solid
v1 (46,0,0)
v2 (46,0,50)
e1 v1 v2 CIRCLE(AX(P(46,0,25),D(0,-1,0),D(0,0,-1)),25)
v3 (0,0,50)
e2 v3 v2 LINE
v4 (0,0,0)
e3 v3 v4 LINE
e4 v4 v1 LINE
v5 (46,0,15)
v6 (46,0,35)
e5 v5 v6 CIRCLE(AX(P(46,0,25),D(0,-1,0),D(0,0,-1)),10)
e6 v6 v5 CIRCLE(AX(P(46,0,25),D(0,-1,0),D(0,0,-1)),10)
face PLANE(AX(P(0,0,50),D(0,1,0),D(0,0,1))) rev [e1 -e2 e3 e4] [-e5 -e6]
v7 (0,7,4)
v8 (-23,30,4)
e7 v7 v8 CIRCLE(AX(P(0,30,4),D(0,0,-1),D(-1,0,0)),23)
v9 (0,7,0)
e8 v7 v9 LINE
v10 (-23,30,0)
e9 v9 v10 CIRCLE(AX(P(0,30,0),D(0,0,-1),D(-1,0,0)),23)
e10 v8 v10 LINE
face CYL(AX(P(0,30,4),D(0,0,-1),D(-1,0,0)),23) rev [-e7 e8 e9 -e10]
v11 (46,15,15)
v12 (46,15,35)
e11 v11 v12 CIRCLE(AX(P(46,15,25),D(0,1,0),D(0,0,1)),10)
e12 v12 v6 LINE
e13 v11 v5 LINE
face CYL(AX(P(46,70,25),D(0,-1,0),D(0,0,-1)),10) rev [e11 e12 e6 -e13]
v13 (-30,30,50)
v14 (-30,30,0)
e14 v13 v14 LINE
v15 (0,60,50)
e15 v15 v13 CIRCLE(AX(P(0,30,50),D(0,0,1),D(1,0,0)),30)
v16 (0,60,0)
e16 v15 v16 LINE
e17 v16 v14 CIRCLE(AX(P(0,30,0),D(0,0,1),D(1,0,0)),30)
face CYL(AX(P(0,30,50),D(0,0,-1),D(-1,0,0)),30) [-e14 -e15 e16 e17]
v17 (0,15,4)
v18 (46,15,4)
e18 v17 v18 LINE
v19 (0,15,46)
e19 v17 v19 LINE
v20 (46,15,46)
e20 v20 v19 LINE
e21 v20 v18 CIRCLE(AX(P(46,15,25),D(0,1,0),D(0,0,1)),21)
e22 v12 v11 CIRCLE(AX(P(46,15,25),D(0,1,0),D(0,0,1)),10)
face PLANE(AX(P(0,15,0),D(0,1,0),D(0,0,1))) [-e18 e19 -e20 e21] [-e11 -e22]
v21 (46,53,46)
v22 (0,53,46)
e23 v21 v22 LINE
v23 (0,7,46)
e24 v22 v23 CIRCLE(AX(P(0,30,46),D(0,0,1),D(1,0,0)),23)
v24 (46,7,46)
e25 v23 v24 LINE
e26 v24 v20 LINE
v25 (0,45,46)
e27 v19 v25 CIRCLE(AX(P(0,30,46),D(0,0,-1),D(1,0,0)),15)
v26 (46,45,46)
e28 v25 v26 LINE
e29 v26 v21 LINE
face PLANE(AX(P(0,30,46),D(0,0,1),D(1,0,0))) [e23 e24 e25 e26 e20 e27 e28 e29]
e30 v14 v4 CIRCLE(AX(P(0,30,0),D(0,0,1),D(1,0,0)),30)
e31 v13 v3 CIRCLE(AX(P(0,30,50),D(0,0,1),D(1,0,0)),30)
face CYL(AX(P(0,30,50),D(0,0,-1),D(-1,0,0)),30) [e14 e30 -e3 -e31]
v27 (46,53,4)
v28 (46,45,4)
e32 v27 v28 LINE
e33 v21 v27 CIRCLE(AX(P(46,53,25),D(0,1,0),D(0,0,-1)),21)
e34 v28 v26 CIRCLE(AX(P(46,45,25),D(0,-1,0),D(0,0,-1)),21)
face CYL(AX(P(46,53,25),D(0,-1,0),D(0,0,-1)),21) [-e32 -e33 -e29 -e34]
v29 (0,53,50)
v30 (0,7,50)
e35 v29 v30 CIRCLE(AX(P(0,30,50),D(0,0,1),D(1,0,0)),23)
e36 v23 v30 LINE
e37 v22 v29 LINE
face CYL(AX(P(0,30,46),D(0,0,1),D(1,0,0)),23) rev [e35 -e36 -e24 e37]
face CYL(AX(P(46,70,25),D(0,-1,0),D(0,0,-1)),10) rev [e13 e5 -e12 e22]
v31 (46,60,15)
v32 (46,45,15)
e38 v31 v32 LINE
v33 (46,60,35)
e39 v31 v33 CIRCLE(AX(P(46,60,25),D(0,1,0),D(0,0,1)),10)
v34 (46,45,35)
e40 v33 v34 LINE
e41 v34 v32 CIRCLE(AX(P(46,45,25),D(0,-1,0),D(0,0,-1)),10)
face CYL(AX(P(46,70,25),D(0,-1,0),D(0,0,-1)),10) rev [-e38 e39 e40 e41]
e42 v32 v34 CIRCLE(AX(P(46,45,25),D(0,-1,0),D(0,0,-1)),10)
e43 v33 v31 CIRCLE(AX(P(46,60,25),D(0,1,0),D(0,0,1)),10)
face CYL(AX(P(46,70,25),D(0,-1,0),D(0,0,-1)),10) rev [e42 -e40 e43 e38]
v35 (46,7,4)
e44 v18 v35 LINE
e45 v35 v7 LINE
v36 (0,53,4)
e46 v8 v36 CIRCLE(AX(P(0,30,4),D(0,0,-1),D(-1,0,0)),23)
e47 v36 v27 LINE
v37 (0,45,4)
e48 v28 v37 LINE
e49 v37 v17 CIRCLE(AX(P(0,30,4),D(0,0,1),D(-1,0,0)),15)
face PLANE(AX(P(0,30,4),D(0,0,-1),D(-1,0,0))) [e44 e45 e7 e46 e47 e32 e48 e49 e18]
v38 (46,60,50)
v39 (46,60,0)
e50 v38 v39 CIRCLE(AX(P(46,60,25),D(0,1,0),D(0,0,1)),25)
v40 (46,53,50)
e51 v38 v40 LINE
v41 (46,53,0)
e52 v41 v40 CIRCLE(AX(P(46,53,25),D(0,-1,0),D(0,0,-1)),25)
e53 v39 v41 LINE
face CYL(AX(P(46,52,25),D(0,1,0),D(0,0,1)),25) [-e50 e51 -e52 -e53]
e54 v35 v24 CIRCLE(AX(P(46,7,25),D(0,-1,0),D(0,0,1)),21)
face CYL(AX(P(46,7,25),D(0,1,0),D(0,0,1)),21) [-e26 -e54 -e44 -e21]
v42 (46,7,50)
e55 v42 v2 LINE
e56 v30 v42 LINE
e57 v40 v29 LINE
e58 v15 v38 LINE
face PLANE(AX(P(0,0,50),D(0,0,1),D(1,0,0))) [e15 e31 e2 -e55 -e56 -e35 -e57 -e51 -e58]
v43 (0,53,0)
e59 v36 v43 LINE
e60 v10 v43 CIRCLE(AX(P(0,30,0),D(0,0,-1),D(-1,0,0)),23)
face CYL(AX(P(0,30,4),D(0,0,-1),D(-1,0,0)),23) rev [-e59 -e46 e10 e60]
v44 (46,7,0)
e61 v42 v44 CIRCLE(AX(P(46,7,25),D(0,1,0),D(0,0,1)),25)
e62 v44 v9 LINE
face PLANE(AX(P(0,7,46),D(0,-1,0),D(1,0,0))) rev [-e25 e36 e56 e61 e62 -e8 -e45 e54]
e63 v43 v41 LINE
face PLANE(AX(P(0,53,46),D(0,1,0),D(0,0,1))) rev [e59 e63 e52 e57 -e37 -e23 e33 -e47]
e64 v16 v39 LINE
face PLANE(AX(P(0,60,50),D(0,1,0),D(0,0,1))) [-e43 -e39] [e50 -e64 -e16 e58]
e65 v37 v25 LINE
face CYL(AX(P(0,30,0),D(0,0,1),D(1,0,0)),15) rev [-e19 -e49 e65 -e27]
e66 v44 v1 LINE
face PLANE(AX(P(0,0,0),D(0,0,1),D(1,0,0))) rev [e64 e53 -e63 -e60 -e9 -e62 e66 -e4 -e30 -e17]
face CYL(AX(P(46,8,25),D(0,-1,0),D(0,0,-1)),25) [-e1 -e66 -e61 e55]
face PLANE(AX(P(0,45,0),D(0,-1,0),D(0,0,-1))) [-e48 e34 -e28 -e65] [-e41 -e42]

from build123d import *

# Parameters (mm, degrees)
U_FORK_BASE_DEPTH   = 50
U_START             = -50
U_WRAP_LAYER_DEPTH  = 50
WRAP_START          = -4
WRAP_RECESS_1_DEPTH = 4
WRAP_RECESS_2_DEPTH = 4
ARM_PAD_1_DEPTH     = 8
ARM_PAD_2_DEPTH     = 8
ARM_START           = -8
ARM_PAD_3_DEPTH     = 8
ARM_PAD_4_DEPTH     = 8
ARM_PAD_5_DEPTH     = 8
PIN_HOLE_SKETCH_R   = 10
PIN_HOLE_DEPTH      = 70
FACE_RELIEF_1_DEPTH = 1
FACE_START          = -1
FACE_RELIEF_2_DEPTH = 1


with BuildPart() as part:
    # U Fork Profile Sketch → U Fork Base (new body)
    with BuildSketch(Plane.XY):
        with BuildLine():
            ThreePointArc((0, 53), (-23, 30), (0, 7))
            Line((0, 7), (46, 7))
            Line((46, 7), (46, 0))
            Line((46, 0), (0, 0))
            ThreePointArc((0, 0), (-30, 30), (0, 60))
            Line((0, 60), (46, 60))
            Line((46, 60), (46, 53))
            Line((46, 53), (0, 53))
        make_face()
    extrude(amount=U_FORK_BASE_DEPTH)

    # U Wrap Layer Sketch → U Wrap Layer (add)
    with BuildSketch(Plane.XY.offset(50).offset(U_START)):
        with BuildLine():
            Line((0, 53), (46, 53))
            Line((46, 53), (46, 45))
            Line((46, 45), (0, 45))
            ThreePointArc((0, 45), (-15, 30), (0, 15))
            Line((0, 15), (46, 15))
            Line((46, 15), (46, 7))
            Line((46, 7), (0, 7))
            ThreePointArc((0, 7), (-23, 30), (0, 53))
        make_face()
    extrude(amount=U_WRAP_LAYER_DEPTH)

    # Wrap Recess 1 Sketch → Wrap Recess 1 (cut)
    with BuildSketch(Plane.XY.offset(50).offset(WRAP_START)):
        with BuildLine():
            Line((0, 45), (46, 45))
            Line((46, 45), (46, 53))
            Line((46, 53), (0, 53))
            ThreePointArc((0, 53), (-23, 30), (0, 7))
            Line((0, 7), (46, 7))
            Line((46, 7), (46, 15))
            Line((46, 15), (0, 15))
            ThreePointArc((0, 15), (-15, 30), (0, 45))
        make_face()
    extrude(amount=WRAP_RECESS_1_DEPTH, mode=Mode.SUBTRACT)

    # Wrap Recess 2 Sketch → Wrap Recess 2 (cut)
    with BuildSketch(Plane(origin=(0, 0, 0), x_dir=(-1, 0, 0), z_dir=(0, 0, -1))):
        with BuildLine():
            Line((-46, 45), (0, 45))
            ThreePointArc((0, 45), (15, 30), (0, 15))
            Line((0, 15), (-46, 15))
            Line((-46, 15), (-46, 7))
            Line((-46, 7), (0, 7))
            ThreePointArc((0, 7), (23, 30), (0, 53))
            Line((0, 53), (-46, 53))
            Line((-46, 53), (-46, 45))
        make_face()
    extrude(amount=-WRAP_RECESS_2_DEPTH, mode=Mode.SUBTRACT)

    # Arm Pad 1 Sketch → Arm Pad 1 (add)
    with BuildSketch(Plane.XZ.offset(-45)):
        with BuildLine():
            ThreePointArc((46, 10), (61, 25), (46, 40))
            Line((46, 40), (46, 10))
        make_face()
    extrude(amount=-ARM_PAD_1_DEPTH)

    # Arm Pad 2 Sketch → Arm Pad 2 (add)
    with BuildSketch(Plane.XZ.offset(-45)):
        with BuildLine():
            Line((46, 46), (46, 40))
            ThreePointArc((46, 40), (61, 25), (46, 10))
            Line((46, 10), (46, 4))
            ThreePointArc((46, 4), (67, 25), (46, 46))
        make_face()
    extrude(amount=-ARM_PAD_2_DEPTH)

    # Arm Pad 3 Sketch → Arm Pad 3 (add)
    with BuildSketch(Plane(origin=(0, 15, 0), x_dir=(1, 0, 0), z_dir=(0, 1, 0)).offset(ARM_START)):
        with BuildLine():
            ThreePointArc((46, -40), (61, -25), (46, -10))
            Line((46, -10), (46, -40))
        make_face()
        with BuildLine():
            ThreePointArc((46, -46), (67, -25), (46, -4))
            Line((46, -4), (46, -10))
            ThreePointArc((46, -10), (61, -25), (46, -40))
            Line((46, -40), (46, -46))
        make_face()
    extrude(amount=ARM_PAD_3_DEPTH)

    # Arm Pad 4 Sketch → Arm Pad 4 (add)
    with BuildSketch(Plane(origin=(0, 60, 0), x_dir=(1, 0, 0), z_dir=(0, 1, 0)).offset(ARM_START)):
        with BuildLine():
            ThreePointArc((46, -50), (71, -25), (46, 0))
            Line((46, 0), (46, -4))
            ThreePointArc((46, -4), (67, -25), (46, -46))
            Line((46, -46), (46, -50))
        make_face()
        with BuildLine():
            ThreePointArc((46, -46), (67, -25), (46, -4))
            Line((46, -4), (46, -46))
        make_face()
    extrude(amount=ARM_PAD_4_DEPTH)

    # Arm Pad 5 Sketch → Arm Pad 5 (add)
    with BuildSketch(Plane.XZ):
        with BuildLine():
            Line((46, 50), (46, 0))
            ThreePointArc((46, 0), (71, 25), (46, 50))
        make_face()
    extrude(amount=-ARM_PAD_5_DEPTH)

    # Pin Hole Sketch → Pin Hole (cut)
    with BuildSketch(Plane.XZ):
        with Locations(Location((46, 25, 0), (0, 0, 270))):
            Circle(PIN_HOLE_SKETCH_R)
    extrude(amount=-PIN_HOLE_DEPTH, mode=Mode.SUBTRACT)

    # Face Relief 1 Sketch → Face Relief 1 (cut)
    with BuildSketch(Plane.XZ.offset(-52)):
        with BuildLine():
            Line((46, 50), (46, 46))
            ThreePointArc((46, 46), (67, 25), (46, 4))
            Line((46, 4), (46, 0))
            ThreePointArc((46, 0), (71, 25), (46, 50))
        make_face()
    extrude(amount=-FACE_RELIEF_1_DEPTH, mode=Mode.SUBTRACT)

    # Face Relief 2 Sketch → Face Relief 2 (cut)
    with BuildSketch(Plane(origin=(0, 8, 0), x_dir=(1, 0, 0), z_dir=(0, 1, 0)).offset(FACE_START)):
        with BuildLine():
            Line((46, 0), (46, -4))
            ThreePointArc((46, -4), (67, -25), (46, -46))
            Line((46, -46), (46, -50))
            ThreePointArc((46, -50), (71, -25), (46, 0))
        make_face()
    extrude(amount=FACE_RELIEF_2_DEPTH, mode=Mode.SUBTRACT)


solid = part.part
